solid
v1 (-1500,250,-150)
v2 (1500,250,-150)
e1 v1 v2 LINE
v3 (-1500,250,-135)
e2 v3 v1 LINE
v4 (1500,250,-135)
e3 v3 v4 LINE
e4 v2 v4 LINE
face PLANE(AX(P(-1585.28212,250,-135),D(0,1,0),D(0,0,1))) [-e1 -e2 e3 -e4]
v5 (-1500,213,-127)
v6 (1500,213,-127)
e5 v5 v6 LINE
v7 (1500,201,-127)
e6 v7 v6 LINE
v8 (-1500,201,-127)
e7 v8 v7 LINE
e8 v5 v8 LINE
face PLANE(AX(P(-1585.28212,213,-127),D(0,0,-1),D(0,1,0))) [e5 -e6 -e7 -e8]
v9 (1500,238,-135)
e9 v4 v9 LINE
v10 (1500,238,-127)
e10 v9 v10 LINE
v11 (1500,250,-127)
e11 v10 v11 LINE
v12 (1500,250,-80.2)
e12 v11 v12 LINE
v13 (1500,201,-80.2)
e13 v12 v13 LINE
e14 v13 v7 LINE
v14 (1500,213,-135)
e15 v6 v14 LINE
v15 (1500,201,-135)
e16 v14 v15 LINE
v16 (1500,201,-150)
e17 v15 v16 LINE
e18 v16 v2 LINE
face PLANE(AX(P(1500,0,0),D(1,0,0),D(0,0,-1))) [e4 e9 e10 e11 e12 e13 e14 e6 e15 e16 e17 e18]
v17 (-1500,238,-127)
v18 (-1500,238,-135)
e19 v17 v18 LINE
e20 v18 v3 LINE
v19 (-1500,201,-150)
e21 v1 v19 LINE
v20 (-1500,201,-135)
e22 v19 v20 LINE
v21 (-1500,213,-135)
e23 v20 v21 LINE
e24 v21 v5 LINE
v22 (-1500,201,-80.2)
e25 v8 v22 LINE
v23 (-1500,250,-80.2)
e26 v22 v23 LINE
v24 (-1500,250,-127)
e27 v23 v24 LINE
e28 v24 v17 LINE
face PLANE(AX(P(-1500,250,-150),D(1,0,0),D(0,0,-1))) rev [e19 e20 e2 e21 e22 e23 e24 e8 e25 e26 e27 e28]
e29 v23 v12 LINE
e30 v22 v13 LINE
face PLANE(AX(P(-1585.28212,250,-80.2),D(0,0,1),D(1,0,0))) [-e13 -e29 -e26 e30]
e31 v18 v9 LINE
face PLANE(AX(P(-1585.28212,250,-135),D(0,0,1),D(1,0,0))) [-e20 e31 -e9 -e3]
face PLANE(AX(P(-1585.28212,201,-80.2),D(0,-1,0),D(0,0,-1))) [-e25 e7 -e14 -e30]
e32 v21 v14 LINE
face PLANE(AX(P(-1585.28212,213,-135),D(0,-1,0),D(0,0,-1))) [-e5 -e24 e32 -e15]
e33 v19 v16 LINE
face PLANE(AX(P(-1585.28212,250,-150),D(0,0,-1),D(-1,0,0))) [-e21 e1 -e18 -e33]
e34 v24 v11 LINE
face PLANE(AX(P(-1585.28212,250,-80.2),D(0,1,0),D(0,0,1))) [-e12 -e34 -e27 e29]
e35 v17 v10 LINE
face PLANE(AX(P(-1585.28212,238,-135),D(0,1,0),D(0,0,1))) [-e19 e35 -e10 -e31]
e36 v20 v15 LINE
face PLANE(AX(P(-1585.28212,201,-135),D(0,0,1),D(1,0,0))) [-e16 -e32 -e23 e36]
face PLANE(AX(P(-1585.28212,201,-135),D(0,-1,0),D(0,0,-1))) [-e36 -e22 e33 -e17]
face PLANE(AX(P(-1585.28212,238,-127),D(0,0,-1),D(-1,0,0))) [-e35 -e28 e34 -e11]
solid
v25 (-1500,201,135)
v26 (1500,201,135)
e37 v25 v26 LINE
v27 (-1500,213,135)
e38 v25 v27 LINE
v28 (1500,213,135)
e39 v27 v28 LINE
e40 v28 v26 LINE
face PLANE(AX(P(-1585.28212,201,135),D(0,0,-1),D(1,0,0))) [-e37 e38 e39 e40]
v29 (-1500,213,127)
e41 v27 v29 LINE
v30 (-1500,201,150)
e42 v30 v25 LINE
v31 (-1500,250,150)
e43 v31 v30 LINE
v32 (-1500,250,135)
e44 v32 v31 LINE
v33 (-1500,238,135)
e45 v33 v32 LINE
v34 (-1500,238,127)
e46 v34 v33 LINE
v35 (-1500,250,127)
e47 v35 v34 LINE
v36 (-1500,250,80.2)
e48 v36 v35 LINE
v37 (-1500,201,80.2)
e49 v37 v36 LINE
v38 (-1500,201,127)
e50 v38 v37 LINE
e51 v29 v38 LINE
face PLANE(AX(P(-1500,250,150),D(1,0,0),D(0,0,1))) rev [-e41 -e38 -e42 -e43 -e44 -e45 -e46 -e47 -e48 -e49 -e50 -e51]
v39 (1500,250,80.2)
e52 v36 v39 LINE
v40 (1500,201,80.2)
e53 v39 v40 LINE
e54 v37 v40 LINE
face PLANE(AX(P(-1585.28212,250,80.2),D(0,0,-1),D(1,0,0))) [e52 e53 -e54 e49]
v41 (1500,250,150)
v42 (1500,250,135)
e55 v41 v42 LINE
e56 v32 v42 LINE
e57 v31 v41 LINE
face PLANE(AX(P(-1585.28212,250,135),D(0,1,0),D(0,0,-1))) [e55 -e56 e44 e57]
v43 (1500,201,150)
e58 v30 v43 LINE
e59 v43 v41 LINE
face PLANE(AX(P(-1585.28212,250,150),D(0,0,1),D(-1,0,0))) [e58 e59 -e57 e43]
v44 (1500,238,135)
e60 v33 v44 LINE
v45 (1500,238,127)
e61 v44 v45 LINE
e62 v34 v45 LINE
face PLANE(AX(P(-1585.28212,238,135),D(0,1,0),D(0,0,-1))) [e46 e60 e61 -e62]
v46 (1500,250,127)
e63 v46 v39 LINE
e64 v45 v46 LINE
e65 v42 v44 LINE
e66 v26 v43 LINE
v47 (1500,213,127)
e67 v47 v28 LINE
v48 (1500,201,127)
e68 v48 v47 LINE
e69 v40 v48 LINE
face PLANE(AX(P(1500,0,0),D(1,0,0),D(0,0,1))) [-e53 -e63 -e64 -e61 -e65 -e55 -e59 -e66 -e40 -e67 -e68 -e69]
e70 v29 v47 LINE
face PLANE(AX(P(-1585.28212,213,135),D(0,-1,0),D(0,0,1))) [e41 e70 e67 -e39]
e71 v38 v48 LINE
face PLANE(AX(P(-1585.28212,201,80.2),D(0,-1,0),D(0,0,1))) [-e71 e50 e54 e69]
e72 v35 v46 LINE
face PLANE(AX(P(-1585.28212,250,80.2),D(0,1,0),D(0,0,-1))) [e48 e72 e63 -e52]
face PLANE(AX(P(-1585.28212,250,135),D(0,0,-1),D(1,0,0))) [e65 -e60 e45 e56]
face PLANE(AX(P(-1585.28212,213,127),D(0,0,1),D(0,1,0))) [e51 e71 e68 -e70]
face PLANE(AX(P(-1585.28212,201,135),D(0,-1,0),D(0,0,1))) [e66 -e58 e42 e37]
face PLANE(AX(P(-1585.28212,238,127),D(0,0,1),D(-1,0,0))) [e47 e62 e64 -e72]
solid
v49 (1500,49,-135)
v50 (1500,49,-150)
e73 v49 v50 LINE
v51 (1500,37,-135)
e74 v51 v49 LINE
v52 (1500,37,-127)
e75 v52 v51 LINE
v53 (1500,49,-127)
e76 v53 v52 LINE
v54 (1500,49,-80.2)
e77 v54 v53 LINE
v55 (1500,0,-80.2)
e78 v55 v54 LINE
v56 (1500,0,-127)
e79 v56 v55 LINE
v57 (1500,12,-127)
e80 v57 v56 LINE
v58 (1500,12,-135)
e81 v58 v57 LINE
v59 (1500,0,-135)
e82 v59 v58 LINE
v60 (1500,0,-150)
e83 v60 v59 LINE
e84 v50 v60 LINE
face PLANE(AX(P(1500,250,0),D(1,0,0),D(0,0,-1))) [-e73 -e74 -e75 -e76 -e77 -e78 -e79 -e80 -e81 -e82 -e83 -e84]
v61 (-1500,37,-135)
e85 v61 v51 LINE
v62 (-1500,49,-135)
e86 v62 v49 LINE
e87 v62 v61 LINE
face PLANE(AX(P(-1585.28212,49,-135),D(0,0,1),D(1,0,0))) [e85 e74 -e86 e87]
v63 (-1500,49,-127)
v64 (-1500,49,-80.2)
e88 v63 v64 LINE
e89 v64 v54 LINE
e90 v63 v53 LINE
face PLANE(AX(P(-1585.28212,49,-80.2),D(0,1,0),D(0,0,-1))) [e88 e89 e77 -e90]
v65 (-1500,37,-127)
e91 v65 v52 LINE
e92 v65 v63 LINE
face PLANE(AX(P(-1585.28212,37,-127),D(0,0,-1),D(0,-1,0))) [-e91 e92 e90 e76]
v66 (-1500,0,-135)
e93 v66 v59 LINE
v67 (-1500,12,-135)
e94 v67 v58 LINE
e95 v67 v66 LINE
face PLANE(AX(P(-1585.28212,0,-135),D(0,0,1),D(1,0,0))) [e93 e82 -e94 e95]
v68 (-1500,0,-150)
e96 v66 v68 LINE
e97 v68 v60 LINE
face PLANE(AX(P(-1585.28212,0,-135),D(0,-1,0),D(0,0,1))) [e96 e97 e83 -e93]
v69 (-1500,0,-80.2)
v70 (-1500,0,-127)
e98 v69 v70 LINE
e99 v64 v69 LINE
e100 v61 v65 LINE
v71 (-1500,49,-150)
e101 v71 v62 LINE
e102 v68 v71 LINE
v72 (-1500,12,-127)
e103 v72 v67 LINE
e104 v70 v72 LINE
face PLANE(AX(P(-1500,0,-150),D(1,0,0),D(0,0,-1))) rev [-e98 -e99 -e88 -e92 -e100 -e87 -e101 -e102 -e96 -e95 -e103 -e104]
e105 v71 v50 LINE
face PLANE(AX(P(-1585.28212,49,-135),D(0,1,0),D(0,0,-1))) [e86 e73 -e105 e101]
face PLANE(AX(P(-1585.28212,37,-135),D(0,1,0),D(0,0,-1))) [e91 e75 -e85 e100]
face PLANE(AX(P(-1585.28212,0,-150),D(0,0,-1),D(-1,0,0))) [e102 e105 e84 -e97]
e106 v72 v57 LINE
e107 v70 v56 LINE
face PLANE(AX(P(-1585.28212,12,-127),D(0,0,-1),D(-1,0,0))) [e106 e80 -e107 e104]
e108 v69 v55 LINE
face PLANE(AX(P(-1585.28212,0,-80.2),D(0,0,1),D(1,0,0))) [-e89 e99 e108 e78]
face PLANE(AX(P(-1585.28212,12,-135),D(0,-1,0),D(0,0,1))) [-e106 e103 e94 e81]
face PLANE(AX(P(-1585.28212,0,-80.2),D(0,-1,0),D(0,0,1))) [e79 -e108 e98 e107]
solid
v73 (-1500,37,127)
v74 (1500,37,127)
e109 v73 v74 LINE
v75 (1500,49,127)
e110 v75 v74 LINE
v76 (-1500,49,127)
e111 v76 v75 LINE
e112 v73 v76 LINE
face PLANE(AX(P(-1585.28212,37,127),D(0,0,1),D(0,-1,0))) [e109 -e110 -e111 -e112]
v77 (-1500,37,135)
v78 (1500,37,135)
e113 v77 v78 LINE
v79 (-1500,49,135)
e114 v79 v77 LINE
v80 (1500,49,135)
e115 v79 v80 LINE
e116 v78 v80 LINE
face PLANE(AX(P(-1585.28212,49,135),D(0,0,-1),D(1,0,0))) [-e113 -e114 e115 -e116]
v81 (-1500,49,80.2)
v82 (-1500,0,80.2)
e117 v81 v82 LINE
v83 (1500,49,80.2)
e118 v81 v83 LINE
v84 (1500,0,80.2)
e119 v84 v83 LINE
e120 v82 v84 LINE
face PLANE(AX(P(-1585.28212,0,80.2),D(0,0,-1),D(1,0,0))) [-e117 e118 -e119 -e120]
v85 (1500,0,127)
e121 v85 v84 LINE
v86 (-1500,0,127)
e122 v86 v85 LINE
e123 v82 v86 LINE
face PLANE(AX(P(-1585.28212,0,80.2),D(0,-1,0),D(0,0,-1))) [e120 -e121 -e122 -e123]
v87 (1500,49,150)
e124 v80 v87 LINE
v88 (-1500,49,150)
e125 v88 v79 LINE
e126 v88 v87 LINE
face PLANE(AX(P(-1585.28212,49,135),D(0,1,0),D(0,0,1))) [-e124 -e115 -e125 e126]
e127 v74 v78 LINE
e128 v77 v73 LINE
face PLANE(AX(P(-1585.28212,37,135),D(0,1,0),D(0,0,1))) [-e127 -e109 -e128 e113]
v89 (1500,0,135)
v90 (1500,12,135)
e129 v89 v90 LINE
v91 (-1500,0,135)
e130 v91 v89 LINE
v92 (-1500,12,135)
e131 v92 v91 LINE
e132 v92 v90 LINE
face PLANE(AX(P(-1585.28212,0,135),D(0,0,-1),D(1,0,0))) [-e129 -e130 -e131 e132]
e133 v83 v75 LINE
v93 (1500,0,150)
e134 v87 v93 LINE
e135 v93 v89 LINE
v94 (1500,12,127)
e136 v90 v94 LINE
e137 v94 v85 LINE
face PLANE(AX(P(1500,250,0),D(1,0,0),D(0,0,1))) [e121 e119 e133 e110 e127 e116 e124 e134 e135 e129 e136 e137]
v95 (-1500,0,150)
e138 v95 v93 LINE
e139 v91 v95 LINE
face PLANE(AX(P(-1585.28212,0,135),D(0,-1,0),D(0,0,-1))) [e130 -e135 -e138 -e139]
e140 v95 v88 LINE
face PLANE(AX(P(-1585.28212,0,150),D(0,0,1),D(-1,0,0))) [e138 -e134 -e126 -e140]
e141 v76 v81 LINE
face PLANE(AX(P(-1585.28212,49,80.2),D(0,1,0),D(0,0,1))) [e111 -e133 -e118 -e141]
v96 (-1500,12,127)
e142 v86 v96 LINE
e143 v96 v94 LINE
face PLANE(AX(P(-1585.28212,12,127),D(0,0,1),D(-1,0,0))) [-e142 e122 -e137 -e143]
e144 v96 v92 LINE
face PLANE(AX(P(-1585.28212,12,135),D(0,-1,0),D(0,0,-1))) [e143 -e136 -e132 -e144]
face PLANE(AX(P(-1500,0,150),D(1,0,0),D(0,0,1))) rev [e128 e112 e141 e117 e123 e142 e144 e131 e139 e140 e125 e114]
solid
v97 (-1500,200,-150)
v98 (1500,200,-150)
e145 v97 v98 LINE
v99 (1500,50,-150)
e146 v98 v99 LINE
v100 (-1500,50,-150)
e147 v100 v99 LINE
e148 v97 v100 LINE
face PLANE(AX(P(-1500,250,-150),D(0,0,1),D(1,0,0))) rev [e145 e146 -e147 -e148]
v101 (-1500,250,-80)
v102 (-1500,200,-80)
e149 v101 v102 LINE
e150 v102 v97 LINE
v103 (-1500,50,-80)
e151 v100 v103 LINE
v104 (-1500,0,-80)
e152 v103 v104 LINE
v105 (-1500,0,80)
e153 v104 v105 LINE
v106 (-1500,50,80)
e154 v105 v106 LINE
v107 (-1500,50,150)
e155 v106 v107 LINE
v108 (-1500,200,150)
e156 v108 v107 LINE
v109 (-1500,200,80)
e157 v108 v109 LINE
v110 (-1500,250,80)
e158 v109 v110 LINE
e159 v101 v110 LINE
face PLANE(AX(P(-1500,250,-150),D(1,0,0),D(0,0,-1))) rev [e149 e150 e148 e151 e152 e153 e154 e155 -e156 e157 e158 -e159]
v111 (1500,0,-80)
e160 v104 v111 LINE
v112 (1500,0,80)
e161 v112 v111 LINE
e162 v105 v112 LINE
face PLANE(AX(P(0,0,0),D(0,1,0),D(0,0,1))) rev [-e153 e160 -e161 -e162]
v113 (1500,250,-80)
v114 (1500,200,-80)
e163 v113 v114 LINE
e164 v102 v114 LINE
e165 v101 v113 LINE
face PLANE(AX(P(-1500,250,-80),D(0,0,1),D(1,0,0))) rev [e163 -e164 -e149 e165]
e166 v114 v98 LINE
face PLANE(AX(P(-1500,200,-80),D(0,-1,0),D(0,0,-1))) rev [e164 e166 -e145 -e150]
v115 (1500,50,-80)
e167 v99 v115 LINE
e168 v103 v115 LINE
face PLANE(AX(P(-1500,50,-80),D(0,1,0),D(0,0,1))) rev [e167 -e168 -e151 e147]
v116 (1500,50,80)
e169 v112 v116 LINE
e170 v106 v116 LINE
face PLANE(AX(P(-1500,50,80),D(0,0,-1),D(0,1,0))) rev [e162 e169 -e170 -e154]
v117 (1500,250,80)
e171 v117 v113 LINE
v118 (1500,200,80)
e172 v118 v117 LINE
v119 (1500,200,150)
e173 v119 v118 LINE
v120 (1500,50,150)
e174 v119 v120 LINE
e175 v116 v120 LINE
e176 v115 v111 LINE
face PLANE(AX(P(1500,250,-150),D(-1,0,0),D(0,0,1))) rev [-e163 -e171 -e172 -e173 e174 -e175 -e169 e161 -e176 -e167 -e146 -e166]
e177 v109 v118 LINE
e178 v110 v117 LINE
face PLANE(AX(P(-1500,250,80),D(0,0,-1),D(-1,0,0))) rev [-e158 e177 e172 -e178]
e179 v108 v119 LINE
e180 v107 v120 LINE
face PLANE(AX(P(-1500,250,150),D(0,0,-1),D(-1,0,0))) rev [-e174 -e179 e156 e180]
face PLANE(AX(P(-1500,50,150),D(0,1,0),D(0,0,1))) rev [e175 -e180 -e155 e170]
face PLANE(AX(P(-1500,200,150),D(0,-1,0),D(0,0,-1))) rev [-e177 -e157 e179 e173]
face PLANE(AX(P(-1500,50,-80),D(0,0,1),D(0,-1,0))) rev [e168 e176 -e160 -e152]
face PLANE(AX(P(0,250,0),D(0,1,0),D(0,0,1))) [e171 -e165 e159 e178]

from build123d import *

# Parameters (mm, degrees)
SKETCH1_W           = 3000
SKETCH1_H           = 300
BOSS_EXTRUDE1_DEPTH = 250
SKETCH2_W           = 70
SKETCH2_H           = 50
CUT_EXTRUDE1_DEPTH  = 3015.13337462
BOSS_EXTRUDE2_DEPTH = 3000


with BuildPart() as part:
    # Sketch1 → Boss-Extrude1 (new body)
    with BuildSketch(Plane(origin=(0, 0, 0), x_dir=(1, 0, 0), z_dir=(0, 1, 0))):
        Rectangle(SKETCH1_W, SKETCH1_H)
    extrude(amount=BOSS_EXTRUDE1_DEPTH)

    # Sketch2 → Cut-Extrude1 (cut, through all)
    with BuildSketch(Plane(origin=(1500, 0, 0), x_dir=(0, 0, -1), z_dir=(1, 0, 0))):
        with Locations((-115, 225)):
            Rectangle(SKETCH2_W, SKETCH2_H)
        with Locations((-115, 25)):
            Rectangle(SKETCH2_W, SKETCH2_H)
        with Locations((115, 225)):
            Rectangle(SKETCH2_W, SKETCH2_H)
        with Locations((115, 25)):
            Rectangle(SKETCH2_W, SKETCH2_H)
    extrude(amount=-CUT_EXTRUDE1_DEPTH, mode=Mode.SUBTRACT)


with BuildPart() as body_2:
    # Sketch3 → Boss-Extrude2 (new body)
    with BuildSketch(Plane(origin=(1500, 0, 0), x_dir=(0, 0, -1), z_dir=(1, 0, 0))):
        Polygon((135, 250), (135, 238), (127, 238), (127, 250), (80.2, 250), (80.2, 201), (127, 201), (127, 213), (135, 213), (135, 201), (150, 201), (150, 250), align=None)
    extrude(amount=-BOSS_EXTRUDE2_DEPTH)


with BuildPart() as body_3:
    # Mirror3: mirrored copy
    add(body_2.part.mirror(Plane(origin=(0, 125, 0), x_dir=(0, 0, 1), z_dir=(0, -1, 0))))


with BuildPart() as body_4:
    # Mirror4: mirrored copy
    add(body_3.part.mirror(Plane.XY))


with BuildPart() as body_5:
    # Mirror4 2: mirrored copy
    add(body_2.part.mirror(Plane.XY))


solid = Compound([part.part, body_2.part, body_3.part, body_4.part, body_5.part])
